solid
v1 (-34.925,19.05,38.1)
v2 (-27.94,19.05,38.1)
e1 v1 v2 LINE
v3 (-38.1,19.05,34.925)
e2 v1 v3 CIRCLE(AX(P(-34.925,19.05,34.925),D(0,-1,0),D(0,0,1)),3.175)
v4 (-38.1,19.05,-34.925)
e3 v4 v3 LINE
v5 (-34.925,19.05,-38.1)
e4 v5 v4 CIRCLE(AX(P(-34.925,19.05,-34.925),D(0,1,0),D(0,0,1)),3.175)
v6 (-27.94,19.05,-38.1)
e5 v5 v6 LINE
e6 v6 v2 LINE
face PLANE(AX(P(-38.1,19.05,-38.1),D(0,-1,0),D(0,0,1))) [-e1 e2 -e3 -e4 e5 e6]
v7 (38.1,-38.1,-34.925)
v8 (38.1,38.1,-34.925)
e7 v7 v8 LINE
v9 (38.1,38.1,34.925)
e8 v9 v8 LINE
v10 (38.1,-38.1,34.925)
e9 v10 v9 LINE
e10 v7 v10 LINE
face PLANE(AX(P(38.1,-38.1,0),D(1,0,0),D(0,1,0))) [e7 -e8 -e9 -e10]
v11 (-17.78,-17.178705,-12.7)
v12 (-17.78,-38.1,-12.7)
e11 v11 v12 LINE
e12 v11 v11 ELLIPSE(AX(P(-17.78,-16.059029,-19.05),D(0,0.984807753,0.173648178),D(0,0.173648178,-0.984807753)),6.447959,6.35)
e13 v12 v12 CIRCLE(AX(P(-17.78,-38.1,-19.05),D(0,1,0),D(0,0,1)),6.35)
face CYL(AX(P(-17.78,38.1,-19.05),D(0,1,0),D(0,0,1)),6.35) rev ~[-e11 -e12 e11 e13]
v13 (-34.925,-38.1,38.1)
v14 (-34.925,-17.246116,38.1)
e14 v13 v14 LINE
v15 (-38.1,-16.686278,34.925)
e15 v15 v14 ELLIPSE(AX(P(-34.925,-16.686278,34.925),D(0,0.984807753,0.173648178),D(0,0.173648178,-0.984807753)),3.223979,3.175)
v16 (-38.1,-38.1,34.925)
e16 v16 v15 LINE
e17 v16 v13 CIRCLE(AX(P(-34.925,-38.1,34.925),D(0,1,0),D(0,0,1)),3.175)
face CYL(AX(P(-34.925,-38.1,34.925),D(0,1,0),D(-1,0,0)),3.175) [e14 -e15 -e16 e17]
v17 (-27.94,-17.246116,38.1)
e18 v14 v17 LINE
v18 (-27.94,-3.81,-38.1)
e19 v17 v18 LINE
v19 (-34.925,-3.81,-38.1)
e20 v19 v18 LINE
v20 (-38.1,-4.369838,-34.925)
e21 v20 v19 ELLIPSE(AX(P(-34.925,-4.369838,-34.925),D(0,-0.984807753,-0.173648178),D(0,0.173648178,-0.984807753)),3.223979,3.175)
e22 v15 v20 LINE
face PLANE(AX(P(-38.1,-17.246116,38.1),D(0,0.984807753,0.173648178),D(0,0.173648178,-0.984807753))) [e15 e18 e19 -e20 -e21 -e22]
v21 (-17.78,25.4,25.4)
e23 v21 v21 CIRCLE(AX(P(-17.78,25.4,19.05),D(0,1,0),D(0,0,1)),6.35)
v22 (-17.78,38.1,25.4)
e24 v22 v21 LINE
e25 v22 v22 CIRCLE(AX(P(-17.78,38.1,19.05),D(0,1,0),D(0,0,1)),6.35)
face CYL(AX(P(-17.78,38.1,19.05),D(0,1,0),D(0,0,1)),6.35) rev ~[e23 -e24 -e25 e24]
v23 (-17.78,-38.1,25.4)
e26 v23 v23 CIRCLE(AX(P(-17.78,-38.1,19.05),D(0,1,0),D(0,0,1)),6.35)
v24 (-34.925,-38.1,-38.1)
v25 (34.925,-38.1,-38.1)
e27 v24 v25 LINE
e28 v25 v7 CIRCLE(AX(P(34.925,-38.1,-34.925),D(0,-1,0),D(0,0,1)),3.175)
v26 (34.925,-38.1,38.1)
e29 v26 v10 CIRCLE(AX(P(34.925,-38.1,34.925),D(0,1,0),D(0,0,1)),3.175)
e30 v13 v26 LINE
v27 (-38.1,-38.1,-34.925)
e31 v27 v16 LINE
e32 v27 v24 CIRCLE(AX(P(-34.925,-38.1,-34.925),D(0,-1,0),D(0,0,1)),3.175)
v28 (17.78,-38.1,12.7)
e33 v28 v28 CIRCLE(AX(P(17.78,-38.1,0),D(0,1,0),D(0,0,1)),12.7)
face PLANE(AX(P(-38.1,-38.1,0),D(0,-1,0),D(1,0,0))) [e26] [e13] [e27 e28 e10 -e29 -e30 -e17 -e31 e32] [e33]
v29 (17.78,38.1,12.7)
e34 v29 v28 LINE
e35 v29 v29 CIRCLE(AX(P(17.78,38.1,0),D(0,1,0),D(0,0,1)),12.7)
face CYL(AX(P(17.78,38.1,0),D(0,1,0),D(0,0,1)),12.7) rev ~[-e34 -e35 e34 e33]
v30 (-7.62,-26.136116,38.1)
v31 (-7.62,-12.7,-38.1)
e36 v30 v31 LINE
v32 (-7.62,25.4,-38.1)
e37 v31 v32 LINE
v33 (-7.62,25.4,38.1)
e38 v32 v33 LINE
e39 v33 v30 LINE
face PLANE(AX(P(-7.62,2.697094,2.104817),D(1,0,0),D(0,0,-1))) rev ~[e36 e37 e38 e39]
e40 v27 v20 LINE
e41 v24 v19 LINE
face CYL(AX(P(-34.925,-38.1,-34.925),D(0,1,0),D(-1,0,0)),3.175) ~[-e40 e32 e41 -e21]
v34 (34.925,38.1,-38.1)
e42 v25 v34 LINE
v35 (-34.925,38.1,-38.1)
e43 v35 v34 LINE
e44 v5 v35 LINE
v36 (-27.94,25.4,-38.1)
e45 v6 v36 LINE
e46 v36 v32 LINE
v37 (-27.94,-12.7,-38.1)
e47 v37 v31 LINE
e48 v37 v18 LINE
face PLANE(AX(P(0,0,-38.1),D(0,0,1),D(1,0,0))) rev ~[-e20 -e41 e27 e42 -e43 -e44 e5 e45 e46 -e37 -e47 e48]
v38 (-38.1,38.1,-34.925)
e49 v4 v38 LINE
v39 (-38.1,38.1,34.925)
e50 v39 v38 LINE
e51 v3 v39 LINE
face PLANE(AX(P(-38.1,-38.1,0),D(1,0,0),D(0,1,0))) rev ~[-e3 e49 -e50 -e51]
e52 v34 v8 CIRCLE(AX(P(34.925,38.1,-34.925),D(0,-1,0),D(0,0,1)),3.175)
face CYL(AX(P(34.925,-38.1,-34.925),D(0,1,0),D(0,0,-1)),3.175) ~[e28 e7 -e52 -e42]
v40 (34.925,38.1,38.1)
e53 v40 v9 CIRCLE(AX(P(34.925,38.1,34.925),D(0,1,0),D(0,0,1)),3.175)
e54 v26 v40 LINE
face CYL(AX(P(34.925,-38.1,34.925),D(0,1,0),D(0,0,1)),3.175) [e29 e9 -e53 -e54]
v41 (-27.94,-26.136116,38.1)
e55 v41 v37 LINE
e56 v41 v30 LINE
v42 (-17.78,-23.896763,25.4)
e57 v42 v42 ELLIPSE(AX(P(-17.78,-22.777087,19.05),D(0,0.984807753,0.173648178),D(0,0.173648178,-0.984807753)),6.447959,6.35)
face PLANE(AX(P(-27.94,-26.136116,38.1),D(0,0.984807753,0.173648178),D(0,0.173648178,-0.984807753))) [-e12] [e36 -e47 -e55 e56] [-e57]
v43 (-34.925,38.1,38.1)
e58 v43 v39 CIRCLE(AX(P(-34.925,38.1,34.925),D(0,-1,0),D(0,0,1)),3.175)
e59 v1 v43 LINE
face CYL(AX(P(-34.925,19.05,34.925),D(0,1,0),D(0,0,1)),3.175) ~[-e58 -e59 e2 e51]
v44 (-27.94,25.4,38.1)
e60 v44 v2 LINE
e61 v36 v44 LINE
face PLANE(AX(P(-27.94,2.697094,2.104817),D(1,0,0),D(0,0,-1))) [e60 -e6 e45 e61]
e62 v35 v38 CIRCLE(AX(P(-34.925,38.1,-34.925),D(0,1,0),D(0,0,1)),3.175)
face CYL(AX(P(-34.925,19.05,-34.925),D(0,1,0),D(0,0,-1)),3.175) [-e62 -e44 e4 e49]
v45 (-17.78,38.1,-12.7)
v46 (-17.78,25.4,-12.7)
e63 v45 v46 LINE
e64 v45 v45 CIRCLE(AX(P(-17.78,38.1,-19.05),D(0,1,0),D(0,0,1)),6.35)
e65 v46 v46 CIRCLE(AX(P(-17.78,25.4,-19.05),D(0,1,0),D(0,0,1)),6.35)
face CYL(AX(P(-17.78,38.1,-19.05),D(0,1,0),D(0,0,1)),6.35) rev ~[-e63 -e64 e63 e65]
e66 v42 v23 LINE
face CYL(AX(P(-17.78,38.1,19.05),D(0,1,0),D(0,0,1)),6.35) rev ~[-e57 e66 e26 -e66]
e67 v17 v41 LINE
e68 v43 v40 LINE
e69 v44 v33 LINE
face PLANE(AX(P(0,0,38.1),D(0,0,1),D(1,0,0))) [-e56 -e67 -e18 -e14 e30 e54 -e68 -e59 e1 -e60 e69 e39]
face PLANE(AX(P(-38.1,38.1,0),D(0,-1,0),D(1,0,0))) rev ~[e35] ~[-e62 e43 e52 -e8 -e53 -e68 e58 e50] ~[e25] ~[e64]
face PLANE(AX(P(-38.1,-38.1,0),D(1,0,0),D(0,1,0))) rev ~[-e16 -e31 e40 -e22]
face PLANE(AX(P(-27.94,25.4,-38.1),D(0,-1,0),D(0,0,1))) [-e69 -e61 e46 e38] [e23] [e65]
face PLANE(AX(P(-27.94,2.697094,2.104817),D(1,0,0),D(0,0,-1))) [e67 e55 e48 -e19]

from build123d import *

# Parameters (mm, degrees)
BLOCK_PROFILE_SKETCH_W  = 76.2
BLOCK_PROFILE_SKETCH_H  = 76.2
BLOCK_BODY_3IN_DEPTH    = 38.1
ANGLED_SLOT_CUT_DEPTH   = 10.16
SLOT_UNDERCUT_CUT_DEPTH = 20.32
EDGE_FILLETS_R0_125_R   = 3.175
TOP_HOLES_SKETCH_R      = 6.35
TOP_HOLES_SKETCH_R_2    = 12.7
TOP_HOLES_3X_DEPTH      = 94.3255592


with BuildPart() as part:
    # Block Profile Sketch → Block Body 3in (new, symmetric)
    with BuildSketch(Plane.XY):
        Rectangle(BLOCK_PROFILE_SKETCH_W, BLOCK_PROFILE_SKETCH_H)
    extrude(amount=BLOCK_BODY_3IN_DEPTH, both=True)

    # Angled Slot Sketch → Angled Slot Cut (cut)
    with BuildSketch(Plane.ZY.offset(38.1)):
        Polygon((38.1, -17.24611593), (-38.1, -3.81), (-38.1, 19.05), (38.1, 19.05), align=None)
    extrude(amount=-ANGLED_SLOT_CUT_DEPTH, mode=Mode.SUBTRACT)

    # Slot Undercut Sketch → Slot Undercut Cut (cut)
    with BuildSketch(Plane.ZY.offset(27.94)):
        Polygon((-38.1, 25.4), (38.1, 25.4), (38.1, -26.13611593), (-38.1, -12.7), align=None)
    extrude(amount=-SLOT_UNDERCUT_CUT_DEPTH, mode=Mode.SUBTRACT)

    # Edge Fillets R0.125
    edge_fillets_r0_125_edges = [part.edges().sort_by_distance(p)[0] for p in [
        (-38.1, 28.575, 38.1),
        (-38.1, -20.955, -38.1),
        (-38.1, -27.673057965, 38.1),
        (38.1, 0, 38.1),
        (-38.1, 28.575, -38.1),
        (38.1, 0, -38.1),
    ]]
    fillet(edge_fillets_r0_125_edges, radius=EDGE_FILLETS_R0_125_R)

    # Top Holes Sketch → Top Holes 3x (cut, through all)
    with BuildSketch(Plane(origin=(0, 38.1, 0), x_dir=(1, 0, 0), z_dir=(0, 1, 0))):
        with Locations(Location((-17.78, 19.05, 0), (0, 0, 270))):
            Circle(TOP_HOLES_SKETCH_R)
        with Locations(Location((-17.78, -19.05, 0), (0, 0, 270))):
            Circle(TOP_HOLES_SKETCH_R)
        with Locations(Location((17.78, 0, 0), (0, 0, 270))):
            Circle(TOP_HOLES_SKETCH_R_2)
    extrude(amount=-TOP_HOLES_3X_DEPTH, mode=Mode.SUBTRACT)


solid = part.part
